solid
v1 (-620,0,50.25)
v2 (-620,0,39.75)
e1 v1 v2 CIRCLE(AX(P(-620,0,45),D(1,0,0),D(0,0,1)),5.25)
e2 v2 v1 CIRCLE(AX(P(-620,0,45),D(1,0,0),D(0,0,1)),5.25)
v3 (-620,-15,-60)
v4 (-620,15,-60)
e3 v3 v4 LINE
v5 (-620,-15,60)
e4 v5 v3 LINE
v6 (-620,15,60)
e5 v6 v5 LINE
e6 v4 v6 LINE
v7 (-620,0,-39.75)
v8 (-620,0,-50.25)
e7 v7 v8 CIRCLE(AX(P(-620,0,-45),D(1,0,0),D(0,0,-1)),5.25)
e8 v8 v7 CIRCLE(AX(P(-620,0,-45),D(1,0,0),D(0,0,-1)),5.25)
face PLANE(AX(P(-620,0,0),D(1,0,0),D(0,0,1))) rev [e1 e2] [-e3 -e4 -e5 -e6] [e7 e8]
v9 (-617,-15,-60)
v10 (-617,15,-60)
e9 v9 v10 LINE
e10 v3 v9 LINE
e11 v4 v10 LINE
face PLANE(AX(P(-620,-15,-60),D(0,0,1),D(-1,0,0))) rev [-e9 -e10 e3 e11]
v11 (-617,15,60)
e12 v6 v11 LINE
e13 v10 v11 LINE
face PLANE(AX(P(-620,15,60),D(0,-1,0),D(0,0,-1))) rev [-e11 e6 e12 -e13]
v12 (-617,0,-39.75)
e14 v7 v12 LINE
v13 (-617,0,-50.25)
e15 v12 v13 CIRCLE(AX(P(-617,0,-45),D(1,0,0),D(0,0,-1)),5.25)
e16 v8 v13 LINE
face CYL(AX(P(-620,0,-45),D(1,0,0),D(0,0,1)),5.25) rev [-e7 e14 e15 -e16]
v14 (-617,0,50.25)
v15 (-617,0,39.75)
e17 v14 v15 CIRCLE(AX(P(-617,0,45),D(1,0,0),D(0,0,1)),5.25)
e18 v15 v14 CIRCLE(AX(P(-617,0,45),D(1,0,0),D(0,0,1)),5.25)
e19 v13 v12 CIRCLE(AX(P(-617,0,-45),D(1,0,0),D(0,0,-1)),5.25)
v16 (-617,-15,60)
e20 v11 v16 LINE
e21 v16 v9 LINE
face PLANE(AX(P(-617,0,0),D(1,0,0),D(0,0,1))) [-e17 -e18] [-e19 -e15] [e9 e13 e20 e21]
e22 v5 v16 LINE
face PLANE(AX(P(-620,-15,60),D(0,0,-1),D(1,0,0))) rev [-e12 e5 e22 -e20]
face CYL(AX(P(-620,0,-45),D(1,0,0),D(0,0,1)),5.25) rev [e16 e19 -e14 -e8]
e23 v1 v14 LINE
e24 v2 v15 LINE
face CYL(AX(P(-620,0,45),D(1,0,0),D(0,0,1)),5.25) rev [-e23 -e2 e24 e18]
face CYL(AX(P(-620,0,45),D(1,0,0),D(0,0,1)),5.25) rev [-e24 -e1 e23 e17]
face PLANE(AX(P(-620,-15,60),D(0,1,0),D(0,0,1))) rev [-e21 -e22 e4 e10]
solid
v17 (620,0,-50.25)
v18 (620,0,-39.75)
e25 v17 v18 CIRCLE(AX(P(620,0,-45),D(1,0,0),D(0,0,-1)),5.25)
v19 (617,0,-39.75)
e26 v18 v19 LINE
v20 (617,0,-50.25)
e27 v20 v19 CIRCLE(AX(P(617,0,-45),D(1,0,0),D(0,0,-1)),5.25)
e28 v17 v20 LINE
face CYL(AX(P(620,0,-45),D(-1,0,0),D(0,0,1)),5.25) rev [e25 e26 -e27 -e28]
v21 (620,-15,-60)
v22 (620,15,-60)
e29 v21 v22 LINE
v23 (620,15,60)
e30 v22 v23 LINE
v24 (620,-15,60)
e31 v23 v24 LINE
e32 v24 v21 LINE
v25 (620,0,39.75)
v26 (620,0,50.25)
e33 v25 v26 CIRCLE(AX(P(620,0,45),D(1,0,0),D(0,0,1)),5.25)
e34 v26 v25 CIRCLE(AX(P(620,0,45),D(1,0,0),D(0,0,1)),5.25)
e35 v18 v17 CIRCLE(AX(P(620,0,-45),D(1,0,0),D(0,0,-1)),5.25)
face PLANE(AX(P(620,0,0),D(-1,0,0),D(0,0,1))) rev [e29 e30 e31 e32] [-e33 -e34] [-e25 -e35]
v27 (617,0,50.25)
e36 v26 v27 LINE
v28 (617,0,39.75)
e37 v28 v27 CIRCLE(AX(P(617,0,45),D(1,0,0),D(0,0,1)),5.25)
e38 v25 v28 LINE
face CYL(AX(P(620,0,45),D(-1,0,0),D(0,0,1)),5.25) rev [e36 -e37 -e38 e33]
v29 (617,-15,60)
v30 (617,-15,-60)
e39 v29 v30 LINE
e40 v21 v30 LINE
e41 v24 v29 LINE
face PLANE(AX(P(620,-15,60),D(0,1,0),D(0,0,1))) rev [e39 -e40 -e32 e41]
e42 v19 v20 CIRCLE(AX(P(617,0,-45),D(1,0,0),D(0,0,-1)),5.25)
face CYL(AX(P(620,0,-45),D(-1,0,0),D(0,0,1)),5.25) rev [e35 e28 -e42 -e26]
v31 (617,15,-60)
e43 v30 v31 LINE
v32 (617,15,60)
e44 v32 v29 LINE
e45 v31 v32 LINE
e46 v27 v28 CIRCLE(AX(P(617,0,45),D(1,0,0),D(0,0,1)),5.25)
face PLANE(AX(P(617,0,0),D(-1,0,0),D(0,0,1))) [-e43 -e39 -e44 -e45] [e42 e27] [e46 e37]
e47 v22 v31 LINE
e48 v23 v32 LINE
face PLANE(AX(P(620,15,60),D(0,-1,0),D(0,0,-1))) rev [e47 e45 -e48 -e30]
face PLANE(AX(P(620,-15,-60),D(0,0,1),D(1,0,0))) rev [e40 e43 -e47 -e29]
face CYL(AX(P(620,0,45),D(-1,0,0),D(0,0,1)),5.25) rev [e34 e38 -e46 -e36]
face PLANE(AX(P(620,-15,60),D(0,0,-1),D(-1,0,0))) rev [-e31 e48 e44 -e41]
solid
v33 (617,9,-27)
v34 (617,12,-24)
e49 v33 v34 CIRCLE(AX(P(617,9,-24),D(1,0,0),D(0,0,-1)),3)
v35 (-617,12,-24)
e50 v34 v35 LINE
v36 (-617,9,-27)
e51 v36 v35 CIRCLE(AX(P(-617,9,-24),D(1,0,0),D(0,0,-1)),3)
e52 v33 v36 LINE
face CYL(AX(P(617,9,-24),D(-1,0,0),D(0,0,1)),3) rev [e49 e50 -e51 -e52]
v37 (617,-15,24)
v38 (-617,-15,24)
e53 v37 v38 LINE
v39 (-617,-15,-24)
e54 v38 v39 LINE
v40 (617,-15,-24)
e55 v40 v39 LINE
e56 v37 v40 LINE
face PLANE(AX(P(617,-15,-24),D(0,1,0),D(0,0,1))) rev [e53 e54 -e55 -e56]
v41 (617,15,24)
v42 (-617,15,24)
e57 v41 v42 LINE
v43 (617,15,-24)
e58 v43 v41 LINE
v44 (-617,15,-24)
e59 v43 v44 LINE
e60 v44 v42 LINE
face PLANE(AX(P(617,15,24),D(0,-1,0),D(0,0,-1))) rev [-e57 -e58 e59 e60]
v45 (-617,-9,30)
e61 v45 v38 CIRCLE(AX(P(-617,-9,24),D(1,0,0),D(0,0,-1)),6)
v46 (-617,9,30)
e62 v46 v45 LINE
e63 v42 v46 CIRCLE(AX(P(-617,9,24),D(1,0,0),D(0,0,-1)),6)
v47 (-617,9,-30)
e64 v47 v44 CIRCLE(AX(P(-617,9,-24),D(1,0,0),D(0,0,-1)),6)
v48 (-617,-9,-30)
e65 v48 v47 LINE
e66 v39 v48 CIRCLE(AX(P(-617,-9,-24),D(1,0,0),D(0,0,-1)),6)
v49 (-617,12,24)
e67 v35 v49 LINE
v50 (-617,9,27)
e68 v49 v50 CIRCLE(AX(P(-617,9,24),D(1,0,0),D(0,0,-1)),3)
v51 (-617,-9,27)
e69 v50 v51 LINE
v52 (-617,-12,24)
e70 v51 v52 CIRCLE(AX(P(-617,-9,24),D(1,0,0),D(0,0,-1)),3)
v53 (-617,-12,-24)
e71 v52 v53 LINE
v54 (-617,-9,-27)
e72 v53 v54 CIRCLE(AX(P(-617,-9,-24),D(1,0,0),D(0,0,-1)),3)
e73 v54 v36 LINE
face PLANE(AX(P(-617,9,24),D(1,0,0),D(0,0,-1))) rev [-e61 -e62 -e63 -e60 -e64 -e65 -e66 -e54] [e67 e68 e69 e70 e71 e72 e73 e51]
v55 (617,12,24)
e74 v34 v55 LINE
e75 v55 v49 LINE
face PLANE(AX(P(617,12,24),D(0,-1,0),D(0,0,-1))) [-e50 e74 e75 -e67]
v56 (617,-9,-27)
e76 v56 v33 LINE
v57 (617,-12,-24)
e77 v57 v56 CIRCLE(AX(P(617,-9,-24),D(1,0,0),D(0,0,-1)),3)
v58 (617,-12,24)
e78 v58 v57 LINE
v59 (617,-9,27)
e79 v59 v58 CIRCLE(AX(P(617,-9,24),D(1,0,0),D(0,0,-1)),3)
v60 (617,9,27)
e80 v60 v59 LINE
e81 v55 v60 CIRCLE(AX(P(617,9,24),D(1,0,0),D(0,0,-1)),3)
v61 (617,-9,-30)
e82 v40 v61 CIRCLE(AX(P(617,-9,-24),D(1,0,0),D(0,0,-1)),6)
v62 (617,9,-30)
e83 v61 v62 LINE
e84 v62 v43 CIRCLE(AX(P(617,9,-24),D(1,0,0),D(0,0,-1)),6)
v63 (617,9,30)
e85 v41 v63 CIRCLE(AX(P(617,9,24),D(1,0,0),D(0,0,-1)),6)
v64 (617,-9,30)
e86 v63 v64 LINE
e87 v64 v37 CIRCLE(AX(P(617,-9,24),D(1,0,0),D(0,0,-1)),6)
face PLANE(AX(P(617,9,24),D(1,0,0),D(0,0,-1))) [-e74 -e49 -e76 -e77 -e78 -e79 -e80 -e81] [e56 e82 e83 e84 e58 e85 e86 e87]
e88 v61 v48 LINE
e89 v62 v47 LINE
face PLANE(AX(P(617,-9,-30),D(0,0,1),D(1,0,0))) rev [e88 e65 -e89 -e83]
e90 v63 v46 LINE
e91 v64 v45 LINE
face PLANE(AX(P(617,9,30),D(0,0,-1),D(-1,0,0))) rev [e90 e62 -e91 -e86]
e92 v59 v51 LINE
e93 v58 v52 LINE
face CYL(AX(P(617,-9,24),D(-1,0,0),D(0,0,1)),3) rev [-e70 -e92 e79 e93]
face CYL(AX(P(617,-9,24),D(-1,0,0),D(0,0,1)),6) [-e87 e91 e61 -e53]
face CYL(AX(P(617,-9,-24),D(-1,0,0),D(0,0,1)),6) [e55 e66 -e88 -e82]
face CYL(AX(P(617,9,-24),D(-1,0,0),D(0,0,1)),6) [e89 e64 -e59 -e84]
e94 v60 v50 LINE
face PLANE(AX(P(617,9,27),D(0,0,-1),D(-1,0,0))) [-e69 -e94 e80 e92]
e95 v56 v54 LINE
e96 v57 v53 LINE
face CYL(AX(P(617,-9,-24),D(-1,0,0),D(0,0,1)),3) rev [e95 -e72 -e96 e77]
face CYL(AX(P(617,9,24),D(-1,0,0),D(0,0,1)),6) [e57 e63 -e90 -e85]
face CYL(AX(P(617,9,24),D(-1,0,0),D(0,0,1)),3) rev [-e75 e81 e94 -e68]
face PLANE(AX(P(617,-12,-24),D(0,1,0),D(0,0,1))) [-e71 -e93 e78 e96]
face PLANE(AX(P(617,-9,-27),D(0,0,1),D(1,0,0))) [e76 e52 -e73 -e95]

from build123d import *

# Parameters (mm, degrees)
MEMBER_1_DEPTH  = 1234
SKETCH_3_W      = 120
SKETCH_3_H      = 30
SKETCH_3_R      = 5.25
EXTRUDE_1_DEPTH = 3


with BuildPart() as part:
    # Sketch1 → Member 1 (new body)
    with BuildSketch(Plane.YZ.offset(-617)):
        with BuildLine():
            Line((-9, -30), (9, -30))
            ThreePointArc((9, -30), (13.242640687, -28.242640687), (15, -24))
            Line((15, -24), (15, 24))
            ThreePointArc((15, 24), (13.242640687, 28.242640687), (9, 30))
            Line((9, 30), (-9, 30))
            ThreePointArc((-9, 30), (-13.242640687, 28.242640687), (-15, 24))
            Line((-15, 24), (-15, -24))
            ThreePointArc((-15, -24), (-13.242640687, -28.242640687), (-9, -30))
        make_face()
        with BuildLine():
            Line((-9, -27), (9, -27))
            ThreePointArc((9, -27), (11.121320344, -26.121320344), (12, -24))
            Line((12, -24), (12, 24))
            ThreePointArc((12, 24), (11.121320344, 26.121320344), (9, 27))
            Line((9, 27), (-9, 27))
            ThreePointArc((-9, 27), (-11.121320344, 26.121320344), (-12, 24))
            Line((-12, 24), (-12, -24))
            ThreePointArc((-12, -24), (-11.121320344, -26.121320344), (-9, -27))
        make_face(mode=Mode.SUBTRACT)
    extrude(amount=MEMBER_1_DEPTH)


with BuildPart() as body_2:
    # 草图3 → 凸台-拉伸1 (new body)
    with BuildSketch(Plane(origin=(617, 0, 0), x_dir=(0, 0, -1), z_dir=(1, 0, 0))):
        Rectangle(SKETCH_3_W, SKETCH_3_H)
        with Locations((45, 0)):
            Circle(SKETCH_3_R, mode=Mode.SUBTRACT)
        with Locations(Location((-45, 0, 0), (0, 0, 180))):
            Circle(SKETCH_3_R, mode=Mode.SUBTRACT)
    extrude(amount=EXTRUDE_1_DEPTH)


with BuildPart() as body_3:
    # 镜向1: mirrored copy
    add(body_2.part.mirror(Plane(origin=(0, 0, 0), x_dir=(0, 0, 1), z_dir=(1, 0, 0))))


solid = Compound([part.part, body_2.part, body_3.part])
